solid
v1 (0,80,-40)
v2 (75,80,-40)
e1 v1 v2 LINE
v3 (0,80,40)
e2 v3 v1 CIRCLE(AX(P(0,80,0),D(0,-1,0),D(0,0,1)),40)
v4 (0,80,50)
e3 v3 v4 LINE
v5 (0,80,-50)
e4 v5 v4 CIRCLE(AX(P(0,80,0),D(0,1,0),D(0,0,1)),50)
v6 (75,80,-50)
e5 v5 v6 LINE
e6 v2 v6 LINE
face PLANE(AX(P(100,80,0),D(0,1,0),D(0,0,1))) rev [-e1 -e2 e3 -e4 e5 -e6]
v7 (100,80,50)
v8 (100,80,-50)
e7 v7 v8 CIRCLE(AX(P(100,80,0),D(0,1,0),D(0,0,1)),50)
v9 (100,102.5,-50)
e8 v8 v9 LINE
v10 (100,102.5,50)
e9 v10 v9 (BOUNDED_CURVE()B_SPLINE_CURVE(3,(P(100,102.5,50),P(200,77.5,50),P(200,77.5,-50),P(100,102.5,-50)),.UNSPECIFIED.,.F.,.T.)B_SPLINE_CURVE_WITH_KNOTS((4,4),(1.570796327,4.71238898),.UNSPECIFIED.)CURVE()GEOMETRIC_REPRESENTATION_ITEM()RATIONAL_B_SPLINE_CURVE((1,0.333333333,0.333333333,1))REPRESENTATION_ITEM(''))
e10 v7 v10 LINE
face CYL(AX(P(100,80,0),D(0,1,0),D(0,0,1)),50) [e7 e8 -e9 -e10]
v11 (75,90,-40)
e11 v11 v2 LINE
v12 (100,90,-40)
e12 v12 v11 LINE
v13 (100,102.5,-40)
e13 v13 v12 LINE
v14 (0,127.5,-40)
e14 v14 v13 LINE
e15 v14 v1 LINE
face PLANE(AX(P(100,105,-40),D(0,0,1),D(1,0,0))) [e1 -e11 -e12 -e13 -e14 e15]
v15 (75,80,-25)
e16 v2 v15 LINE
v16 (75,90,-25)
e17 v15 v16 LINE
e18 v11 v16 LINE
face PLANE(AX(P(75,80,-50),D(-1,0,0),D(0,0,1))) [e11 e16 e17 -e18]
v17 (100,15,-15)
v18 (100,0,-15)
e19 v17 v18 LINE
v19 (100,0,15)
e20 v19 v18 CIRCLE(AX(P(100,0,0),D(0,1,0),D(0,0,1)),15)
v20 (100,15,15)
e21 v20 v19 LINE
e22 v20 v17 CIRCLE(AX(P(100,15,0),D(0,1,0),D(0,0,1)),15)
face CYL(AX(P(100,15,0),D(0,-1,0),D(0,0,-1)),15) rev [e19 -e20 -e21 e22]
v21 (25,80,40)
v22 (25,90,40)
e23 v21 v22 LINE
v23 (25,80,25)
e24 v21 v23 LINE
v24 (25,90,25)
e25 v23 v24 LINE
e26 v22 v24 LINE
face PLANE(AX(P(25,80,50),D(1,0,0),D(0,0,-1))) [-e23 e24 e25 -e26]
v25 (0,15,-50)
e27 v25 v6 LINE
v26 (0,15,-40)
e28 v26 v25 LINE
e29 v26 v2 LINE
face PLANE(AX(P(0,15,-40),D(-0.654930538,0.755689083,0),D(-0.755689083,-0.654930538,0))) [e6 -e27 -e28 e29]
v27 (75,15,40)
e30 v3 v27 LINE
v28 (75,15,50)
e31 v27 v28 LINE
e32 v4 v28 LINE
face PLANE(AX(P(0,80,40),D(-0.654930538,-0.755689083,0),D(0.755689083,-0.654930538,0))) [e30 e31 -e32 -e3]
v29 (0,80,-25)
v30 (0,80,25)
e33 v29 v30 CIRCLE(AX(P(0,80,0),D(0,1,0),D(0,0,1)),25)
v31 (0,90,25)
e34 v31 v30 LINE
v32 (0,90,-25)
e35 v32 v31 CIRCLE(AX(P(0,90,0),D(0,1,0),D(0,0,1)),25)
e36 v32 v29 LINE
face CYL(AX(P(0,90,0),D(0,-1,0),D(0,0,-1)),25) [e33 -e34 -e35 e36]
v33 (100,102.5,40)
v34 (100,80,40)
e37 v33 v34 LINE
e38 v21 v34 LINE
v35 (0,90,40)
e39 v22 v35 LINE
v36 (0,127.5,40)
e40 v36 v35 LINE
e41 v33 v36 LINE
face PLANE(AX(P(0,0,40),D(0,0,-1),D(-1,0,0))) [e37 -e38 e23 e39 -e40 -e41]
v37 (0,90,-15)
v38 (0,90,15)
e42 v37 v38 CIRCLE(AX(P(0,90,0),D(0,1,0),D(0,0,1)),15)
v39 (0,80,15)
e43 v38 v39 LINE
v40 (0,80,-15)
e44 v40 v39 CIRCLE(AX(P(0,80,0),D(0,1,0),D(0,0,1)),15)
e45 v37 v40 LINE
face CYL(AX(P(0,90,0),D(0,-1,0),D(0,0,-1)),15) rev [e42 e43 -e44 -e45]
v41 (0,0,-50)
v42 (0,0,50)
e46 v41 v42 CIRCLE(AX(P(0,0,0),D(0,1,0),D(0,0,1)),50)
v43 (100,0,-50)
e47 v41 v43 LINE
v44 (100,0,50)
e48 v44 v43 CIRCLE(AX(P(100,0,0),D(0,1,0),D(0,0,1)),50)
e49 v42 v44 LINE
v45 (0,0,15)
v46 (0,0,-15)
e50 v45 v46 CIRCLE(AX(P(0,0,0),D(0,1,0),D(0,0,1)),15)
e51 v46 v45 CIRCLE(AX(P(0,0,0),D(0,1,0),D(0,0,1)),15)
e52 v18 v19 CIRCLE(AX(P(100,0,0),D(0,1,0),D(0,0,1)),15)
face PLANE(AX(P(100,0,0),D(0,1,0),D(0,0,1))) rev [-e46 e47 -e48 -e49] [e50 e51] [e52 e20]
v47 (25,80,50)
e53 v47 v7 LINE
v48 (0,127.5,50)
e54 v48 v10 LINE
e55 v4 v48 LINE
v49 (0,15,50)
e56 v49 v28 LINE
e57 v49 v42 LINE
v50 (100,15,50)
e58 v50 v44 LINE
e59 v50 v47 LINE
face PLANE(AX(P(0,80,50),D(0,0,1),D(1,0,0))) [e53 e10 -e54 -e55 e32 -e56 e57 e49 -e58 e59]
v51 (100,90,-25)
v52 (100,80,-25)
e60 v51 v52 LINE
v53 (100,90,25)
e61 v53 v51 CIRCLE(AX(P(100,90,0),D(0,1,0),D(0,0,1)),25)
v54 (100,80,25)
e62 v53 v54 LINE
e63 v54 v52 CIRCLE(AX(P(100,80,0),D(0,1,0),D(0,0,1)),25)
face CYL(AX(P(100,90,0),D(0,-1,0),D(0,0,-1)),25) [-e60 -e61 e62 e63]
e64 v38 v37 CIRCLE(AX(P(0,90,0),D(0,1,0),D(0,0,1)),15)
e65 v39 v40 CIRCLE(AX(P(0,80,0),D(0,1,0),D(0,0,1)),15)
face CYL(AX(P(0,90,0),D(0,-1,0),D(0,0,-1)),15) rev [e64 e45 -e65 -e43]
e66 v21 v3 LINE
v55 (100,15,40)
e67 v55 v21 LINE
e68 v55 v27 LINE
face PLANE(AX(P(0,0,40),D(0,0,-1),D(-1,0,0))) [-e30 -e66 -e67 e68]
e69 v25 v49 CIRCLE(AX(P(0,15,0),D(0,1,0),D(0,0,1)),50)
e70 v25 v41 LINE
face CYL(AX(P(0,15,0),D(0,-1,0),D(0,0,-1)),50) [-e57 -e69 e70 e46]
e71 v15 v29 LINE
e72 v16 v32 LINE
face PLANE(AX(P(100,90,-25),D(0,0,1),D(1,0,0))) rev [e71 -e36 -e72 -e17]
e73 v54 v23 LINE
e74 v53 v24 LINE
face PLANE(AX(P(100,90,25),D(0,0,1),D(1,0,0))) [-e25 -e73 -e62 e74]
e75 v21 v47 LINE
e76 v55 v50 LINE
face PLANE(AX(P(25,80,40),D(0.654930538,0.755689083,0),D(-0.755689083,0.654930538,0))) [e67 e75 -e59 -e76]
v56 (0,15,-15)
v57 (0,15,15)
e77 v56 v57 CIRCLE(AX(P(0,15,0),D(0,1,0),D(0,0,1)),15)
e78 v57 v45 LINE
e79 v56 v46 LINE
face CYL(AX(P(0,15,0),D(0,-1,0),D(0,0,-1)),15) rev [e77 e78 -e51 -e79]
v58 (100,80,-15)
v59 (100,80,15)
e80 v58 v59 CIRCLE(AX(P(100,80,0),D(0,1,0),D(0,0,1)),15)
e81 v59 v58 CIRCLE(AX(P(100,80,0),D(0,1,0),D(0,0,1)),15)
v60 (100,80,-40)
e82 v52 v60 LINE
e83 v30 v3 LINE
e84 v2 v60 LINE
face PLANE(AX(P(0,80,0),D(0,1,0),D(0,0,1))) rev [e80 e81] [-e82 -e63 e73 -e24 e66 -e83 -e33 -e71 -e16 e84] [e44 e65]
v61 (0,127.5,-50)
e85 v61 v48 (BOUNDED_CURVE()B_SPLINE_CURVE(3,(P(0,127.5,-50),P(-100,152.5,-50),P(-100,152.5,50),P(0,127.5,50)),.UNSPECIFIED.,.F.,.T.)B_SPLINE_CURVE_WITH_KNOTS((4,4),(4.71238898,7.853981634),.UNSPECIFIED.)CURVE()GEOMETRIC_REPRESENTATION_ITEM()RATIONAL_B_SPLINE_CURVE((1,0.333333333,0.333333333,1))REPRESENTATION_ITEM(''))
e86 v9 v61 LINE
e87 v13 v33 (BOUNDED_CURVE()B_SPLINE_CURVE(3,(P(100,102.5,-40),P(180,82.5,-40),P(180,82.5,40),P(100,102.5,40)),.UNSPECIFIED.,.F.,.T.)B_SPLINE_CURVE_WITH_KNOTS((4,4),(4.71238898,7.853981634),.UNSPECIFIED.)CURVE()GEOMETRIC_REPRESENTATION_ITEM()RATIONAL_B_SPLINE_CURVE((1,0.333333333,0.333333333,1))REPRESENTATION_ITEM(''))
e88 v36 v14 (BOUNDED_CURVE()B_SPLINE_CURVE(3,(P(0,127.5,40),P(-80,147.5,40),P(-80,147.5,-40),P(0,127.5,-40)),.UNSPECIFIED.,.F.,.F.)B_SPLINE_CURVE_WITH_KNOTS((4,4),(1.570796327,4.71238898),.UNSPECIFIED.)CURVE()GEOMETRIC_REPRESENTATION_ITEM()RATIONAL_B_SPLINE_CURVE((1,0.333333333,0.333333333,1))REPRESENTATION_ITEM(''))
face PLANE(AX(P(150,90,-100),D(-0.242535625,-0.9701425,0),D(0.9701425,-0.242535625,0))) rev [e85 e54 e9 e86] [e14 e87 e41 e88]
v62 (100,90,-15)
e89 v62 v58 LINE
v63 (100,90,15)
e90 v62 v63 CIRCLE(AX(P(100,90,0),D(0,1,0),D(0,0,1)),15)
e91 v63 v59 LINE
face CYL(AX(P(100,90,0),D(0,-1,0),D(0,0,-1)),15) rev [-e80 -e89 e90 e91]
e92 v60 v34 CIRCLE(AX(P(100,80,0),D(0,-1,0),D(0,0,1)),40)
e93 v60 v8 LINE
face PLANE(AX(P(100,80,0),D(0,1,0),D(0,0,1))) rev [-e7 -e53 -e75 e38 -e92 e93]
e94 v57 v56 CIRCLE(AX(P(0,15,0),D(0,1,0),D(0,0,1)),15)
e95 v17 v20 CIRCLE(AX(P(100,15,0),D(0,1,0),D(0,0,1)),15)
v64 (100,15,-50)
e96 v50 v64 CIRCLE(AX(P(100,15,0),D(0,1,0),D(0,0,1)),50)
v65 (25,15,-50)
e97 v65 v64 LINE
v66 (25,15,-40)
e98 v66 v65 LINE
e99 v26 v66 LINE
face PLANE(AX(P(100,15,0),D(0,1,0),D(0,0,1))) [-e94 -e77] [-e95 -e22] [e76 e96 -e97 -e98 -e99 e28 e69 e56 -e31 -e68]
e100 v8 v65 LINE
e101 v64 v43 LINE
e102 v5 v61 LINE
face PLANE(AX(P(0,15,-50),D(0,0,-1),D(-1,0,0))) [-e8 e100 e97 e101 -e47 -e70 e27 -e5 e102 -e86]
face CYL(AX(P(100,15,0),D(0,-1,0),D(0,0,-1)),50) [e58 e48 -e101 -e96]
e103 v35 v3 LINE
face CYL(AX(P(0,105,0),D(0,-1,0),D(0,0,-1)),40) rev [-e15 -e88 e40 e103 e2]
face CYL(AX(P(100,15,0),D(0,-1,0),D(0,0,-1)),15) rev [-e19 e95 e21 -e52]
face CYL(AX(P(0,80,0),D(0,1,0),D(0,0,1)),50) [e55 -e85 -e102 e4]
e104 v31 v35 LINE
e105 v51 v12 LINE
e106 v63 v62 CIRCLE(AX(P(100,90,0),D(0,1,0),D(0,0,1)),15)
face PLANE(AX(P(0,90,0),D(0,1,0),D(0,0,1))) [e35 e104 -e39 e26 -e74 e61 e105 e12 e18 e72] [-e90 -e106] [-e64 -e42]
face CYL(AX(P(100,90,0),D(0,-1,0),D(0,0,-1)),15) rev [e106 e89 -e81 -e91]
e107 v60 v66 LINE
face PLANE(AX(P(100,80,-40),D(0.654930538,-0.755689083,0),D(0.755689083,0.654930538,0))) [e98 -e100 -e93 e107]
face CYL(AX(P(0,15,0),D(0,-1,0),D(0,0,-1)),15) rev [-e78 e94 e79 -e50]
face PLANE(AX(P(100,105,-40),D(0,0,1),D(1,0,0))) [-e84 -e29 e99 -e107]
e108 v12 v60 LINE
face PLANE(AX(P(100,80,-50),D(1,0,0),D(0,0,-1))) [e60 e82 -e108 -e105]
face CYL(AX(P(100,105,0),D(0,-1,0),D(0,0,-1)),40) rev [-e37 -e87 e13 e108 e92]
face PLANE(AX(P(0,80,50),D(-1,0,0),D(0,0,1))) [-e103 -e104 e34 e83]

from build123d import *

# Parameters (mm, degrees)
LINK_PROFILES_SKETCH_R   = 15
BASE_LINK_PLATE_DEPTH    = 15
UPPER_START              = 90
UPPER_LINK_PLATE_DEPTH   = 10
LINK_START               = 15
LINK_SLOT_CUT_DEPTH      = 90
SLOT_START               = 80
SKETCH1_7_R              = 15
SLOT_TAB_BOSS_DEPTH      = 10
BRACE_STRUT_A_DEPTH      = 10
BRACE_WEB_A_SKETCH_W     = 25
BRACE_WEB_A_SKETCH_H     = 25
BRACE_WEB_A_DEPTH        = 10
BRACE_STRUT_B_DEPTH      = 10
BRACE_WEB_B_SKETCH_W     = 25
BRACE_WEB_B_SKETCH_H     = 25
BRACE_WEB_B_DEPTH        = 10
SLOTTED_START            = 90
SLOTTED_UPPER_WALL_DEPTH = 50
SIDE_TRIM_CUT_DEPTH      = 150


with BuildPart() as part:
    # Link Profiles Sketch → Base Link Plate (new body)
    with BuildSketch(Plane(origin=(0, 0, 0), x_dir=(1, 0, 0), z_dir=(0, 1, 0))):
        with BuildLine():
            Line((0, 50), (100, 50))
            ThreePointArc((100, 50), (150, 0), (100, -50))
            Line((100, -50), (0, -50))
            ThreePointArc((0, -50), (-50, 0), (0, 50))
        make_face()
        with Locations(Location((0, 0, 0), (0, 0, 270))):
            Circle(LINK_PROFILES_SKETCH_R, mode=Mode.SUBTRACT)
        with Locations(Location((100, 0, 0), (0, 0, 270))):
            Circle(LINK_PROFILES_SKETCH_R, mode=Mode.SUBTRACT)
    extrude(amount=BASE_LINK_PLATE_DEPTH)



with BuildPart() as body_2:
    # Sketch1_5 → Upper Link Plate (new body)
    with BuildSketch(Plane(origin=(0, 0, 0), x_dir=(1, 0, 0), z_dir=(0, 1, 0)).offset(UPPER_START)):
        with BuildLine():
            Line((0, 50), (100, 50))
            ThreePointArc((100, 50), (150, 0), (100, -50))
            Line((100, -50), (0, -50))
            ThreePointArc((0, -50), (-50, 0), (0, 50))
        make_face()
    extrude(amount=-UPPER_LINK_PLATE_DEPTH)

    # Sketch1_6 → Link Slot Cut (cut)
    with BuildSketch(Plane(origin=(0, 0, 0), x_dir=(1, 0, 0), z_dir=(0, 1, 0)).offset(LINK_START)):
        with BuildLine():
            Line((0, 40), (100, 40))
            ThreePointArc((100, 40), (140, 0), (100, -40))
            Line((100, -40), (0, -40))
            ThreePointArc((0, -40), (-40, 0), (0, 40))
        make_face()
    extrude(amount=LINK_SLOT_CUT_DEPTH, mode=Mode.SUBTRACT)


with BuildPart() as body_3:
    # Sketch1_7 → Slot Tab Boss (new body)
    with BuildSketch(Plane(origin=(0, 0, 0), x_dir=(1, 0, 0), z_dir=(0, 1, 0)).offset(SLOT_START)):
        with BuildLine():
            Line((0, 25), (100, 25))
            ThreePointArc((100, 25), (125, 0), (100, -25))
            Line((100, -25), (0, -25))
            ThreePointArc((0, -25), (-25, 0), (0, 25))
        make_face()
        with Locations(Location((0, 0, 0), (0, 0, 270))):
            Circle(SKETCH1_7_R, mode=Mode.SUBTRACT)
        with Locations(Location((100, 0, 0), (0, 0, 270))):
            Circle(SKETCH1_7_R, mode=Mode.SUBTRACT)
    extrude(amount=SLOT_TAB_BOSS_DEPTH)


with BuildPart() as part_1:
    add(part.part)

    add(body_2.part)  # Brace Strut A merges body 2
    # Brace Strut A Sketch → Brace Strut A (add)
    with BuildSketch(Plane.XY.offset(50)):
        Polygon((100, 0), (75, 0), (75, 15), (0, 80), (0, 90), (25, 90), (25, 80), (100, 15), align=None)
    extrude(amount=-BRACE_STRUT_A_DEPTH)


    add(body_3.part)  # Brace Web A merges body 3
    # Brace Web A Sketch → Brace Web A (add)
    with BuildSketch(Plane(origin=(0, 90, 0), x_dir=(1, 0, 0), z_dir=(0, 1, 0))):
        with Locations((12.5, -37.5)):
            Rectangle(BRACE_WEB_A_SKETCH_W, BRACE_WEB_A_SKETCH_H)
    extrude(amount=-BRACE_WEB_A_DEPTH)

    # Brace Strut B Sketch → Brace Strut B (add)
    with BuildSketch(Plane(origin=(0, 0, -50), x_dir=(-1, 0, 0), z_dir=(0, 0, -1))):
        Polygon((0, 0), (-25, 0), (-25, 15), (-100, 80), (-100, 90), (-75, 90), (-75, 80), (0, 15), align=None)
    extrude(amount=-BRACE_STRUT_B_DEPTH)

    # Brace Web B Sketch → Brace Web B (add)
    with BuildSketch(Plane(origin=(0, 90, 0), x_dir=(1, 0, 0), z_dir=(0, 1, 0))):
        with Locations((87.5, 37.5)):
            Rectangle(BRACE_WEB_B_SKETCH_W, BRACE_WEB_B_SKETCH_H)
    extrude(amount=-BRACE_WEB_B_DEPTH)

    # Sketch1_9 → Slotted Upper Wall (add)
    with BuildSketch(Plane(origin=(0, 0, 0), x_dir=(1, 0, 0), z_dir=(0, 1, 0)).offset(SLOTTED_START)):
        with BuildLine():
            Line((0, 50), (100, 50))
            ThreePointArc((100, 50), (150, 0), (100, -50))
            Line((100, -50), (0, -50))
            ThreePointArc((0, -50), (-50, 0), (0, 50))
        make_face()
        with BuildLine():
            Line((0, 40), (100, 40))
            ThreePointArc((100, 40), (140, 0), (100, -40))
            Line((100, -40), (0, -40))
            ThreePointArc((0, -40), (-40, 0), (0, 40))
        make_face(mode=Mode.SUBTRACT)
    extrude(amount=SLOTTED_UPPER_WALL_DEPTH)

    # Side Trim Sketch → Side Trim Cut (cut)
    with BuildSketch(Plane.XY.offset(50)):
        Polygon((150, 90), (-50, 140), (150, 140), align=None)
    extrude(amount=-SIDE_TRIM_CUT_DEPTH, mode=Mode.SUBTRACT)


solid = part_1.part
